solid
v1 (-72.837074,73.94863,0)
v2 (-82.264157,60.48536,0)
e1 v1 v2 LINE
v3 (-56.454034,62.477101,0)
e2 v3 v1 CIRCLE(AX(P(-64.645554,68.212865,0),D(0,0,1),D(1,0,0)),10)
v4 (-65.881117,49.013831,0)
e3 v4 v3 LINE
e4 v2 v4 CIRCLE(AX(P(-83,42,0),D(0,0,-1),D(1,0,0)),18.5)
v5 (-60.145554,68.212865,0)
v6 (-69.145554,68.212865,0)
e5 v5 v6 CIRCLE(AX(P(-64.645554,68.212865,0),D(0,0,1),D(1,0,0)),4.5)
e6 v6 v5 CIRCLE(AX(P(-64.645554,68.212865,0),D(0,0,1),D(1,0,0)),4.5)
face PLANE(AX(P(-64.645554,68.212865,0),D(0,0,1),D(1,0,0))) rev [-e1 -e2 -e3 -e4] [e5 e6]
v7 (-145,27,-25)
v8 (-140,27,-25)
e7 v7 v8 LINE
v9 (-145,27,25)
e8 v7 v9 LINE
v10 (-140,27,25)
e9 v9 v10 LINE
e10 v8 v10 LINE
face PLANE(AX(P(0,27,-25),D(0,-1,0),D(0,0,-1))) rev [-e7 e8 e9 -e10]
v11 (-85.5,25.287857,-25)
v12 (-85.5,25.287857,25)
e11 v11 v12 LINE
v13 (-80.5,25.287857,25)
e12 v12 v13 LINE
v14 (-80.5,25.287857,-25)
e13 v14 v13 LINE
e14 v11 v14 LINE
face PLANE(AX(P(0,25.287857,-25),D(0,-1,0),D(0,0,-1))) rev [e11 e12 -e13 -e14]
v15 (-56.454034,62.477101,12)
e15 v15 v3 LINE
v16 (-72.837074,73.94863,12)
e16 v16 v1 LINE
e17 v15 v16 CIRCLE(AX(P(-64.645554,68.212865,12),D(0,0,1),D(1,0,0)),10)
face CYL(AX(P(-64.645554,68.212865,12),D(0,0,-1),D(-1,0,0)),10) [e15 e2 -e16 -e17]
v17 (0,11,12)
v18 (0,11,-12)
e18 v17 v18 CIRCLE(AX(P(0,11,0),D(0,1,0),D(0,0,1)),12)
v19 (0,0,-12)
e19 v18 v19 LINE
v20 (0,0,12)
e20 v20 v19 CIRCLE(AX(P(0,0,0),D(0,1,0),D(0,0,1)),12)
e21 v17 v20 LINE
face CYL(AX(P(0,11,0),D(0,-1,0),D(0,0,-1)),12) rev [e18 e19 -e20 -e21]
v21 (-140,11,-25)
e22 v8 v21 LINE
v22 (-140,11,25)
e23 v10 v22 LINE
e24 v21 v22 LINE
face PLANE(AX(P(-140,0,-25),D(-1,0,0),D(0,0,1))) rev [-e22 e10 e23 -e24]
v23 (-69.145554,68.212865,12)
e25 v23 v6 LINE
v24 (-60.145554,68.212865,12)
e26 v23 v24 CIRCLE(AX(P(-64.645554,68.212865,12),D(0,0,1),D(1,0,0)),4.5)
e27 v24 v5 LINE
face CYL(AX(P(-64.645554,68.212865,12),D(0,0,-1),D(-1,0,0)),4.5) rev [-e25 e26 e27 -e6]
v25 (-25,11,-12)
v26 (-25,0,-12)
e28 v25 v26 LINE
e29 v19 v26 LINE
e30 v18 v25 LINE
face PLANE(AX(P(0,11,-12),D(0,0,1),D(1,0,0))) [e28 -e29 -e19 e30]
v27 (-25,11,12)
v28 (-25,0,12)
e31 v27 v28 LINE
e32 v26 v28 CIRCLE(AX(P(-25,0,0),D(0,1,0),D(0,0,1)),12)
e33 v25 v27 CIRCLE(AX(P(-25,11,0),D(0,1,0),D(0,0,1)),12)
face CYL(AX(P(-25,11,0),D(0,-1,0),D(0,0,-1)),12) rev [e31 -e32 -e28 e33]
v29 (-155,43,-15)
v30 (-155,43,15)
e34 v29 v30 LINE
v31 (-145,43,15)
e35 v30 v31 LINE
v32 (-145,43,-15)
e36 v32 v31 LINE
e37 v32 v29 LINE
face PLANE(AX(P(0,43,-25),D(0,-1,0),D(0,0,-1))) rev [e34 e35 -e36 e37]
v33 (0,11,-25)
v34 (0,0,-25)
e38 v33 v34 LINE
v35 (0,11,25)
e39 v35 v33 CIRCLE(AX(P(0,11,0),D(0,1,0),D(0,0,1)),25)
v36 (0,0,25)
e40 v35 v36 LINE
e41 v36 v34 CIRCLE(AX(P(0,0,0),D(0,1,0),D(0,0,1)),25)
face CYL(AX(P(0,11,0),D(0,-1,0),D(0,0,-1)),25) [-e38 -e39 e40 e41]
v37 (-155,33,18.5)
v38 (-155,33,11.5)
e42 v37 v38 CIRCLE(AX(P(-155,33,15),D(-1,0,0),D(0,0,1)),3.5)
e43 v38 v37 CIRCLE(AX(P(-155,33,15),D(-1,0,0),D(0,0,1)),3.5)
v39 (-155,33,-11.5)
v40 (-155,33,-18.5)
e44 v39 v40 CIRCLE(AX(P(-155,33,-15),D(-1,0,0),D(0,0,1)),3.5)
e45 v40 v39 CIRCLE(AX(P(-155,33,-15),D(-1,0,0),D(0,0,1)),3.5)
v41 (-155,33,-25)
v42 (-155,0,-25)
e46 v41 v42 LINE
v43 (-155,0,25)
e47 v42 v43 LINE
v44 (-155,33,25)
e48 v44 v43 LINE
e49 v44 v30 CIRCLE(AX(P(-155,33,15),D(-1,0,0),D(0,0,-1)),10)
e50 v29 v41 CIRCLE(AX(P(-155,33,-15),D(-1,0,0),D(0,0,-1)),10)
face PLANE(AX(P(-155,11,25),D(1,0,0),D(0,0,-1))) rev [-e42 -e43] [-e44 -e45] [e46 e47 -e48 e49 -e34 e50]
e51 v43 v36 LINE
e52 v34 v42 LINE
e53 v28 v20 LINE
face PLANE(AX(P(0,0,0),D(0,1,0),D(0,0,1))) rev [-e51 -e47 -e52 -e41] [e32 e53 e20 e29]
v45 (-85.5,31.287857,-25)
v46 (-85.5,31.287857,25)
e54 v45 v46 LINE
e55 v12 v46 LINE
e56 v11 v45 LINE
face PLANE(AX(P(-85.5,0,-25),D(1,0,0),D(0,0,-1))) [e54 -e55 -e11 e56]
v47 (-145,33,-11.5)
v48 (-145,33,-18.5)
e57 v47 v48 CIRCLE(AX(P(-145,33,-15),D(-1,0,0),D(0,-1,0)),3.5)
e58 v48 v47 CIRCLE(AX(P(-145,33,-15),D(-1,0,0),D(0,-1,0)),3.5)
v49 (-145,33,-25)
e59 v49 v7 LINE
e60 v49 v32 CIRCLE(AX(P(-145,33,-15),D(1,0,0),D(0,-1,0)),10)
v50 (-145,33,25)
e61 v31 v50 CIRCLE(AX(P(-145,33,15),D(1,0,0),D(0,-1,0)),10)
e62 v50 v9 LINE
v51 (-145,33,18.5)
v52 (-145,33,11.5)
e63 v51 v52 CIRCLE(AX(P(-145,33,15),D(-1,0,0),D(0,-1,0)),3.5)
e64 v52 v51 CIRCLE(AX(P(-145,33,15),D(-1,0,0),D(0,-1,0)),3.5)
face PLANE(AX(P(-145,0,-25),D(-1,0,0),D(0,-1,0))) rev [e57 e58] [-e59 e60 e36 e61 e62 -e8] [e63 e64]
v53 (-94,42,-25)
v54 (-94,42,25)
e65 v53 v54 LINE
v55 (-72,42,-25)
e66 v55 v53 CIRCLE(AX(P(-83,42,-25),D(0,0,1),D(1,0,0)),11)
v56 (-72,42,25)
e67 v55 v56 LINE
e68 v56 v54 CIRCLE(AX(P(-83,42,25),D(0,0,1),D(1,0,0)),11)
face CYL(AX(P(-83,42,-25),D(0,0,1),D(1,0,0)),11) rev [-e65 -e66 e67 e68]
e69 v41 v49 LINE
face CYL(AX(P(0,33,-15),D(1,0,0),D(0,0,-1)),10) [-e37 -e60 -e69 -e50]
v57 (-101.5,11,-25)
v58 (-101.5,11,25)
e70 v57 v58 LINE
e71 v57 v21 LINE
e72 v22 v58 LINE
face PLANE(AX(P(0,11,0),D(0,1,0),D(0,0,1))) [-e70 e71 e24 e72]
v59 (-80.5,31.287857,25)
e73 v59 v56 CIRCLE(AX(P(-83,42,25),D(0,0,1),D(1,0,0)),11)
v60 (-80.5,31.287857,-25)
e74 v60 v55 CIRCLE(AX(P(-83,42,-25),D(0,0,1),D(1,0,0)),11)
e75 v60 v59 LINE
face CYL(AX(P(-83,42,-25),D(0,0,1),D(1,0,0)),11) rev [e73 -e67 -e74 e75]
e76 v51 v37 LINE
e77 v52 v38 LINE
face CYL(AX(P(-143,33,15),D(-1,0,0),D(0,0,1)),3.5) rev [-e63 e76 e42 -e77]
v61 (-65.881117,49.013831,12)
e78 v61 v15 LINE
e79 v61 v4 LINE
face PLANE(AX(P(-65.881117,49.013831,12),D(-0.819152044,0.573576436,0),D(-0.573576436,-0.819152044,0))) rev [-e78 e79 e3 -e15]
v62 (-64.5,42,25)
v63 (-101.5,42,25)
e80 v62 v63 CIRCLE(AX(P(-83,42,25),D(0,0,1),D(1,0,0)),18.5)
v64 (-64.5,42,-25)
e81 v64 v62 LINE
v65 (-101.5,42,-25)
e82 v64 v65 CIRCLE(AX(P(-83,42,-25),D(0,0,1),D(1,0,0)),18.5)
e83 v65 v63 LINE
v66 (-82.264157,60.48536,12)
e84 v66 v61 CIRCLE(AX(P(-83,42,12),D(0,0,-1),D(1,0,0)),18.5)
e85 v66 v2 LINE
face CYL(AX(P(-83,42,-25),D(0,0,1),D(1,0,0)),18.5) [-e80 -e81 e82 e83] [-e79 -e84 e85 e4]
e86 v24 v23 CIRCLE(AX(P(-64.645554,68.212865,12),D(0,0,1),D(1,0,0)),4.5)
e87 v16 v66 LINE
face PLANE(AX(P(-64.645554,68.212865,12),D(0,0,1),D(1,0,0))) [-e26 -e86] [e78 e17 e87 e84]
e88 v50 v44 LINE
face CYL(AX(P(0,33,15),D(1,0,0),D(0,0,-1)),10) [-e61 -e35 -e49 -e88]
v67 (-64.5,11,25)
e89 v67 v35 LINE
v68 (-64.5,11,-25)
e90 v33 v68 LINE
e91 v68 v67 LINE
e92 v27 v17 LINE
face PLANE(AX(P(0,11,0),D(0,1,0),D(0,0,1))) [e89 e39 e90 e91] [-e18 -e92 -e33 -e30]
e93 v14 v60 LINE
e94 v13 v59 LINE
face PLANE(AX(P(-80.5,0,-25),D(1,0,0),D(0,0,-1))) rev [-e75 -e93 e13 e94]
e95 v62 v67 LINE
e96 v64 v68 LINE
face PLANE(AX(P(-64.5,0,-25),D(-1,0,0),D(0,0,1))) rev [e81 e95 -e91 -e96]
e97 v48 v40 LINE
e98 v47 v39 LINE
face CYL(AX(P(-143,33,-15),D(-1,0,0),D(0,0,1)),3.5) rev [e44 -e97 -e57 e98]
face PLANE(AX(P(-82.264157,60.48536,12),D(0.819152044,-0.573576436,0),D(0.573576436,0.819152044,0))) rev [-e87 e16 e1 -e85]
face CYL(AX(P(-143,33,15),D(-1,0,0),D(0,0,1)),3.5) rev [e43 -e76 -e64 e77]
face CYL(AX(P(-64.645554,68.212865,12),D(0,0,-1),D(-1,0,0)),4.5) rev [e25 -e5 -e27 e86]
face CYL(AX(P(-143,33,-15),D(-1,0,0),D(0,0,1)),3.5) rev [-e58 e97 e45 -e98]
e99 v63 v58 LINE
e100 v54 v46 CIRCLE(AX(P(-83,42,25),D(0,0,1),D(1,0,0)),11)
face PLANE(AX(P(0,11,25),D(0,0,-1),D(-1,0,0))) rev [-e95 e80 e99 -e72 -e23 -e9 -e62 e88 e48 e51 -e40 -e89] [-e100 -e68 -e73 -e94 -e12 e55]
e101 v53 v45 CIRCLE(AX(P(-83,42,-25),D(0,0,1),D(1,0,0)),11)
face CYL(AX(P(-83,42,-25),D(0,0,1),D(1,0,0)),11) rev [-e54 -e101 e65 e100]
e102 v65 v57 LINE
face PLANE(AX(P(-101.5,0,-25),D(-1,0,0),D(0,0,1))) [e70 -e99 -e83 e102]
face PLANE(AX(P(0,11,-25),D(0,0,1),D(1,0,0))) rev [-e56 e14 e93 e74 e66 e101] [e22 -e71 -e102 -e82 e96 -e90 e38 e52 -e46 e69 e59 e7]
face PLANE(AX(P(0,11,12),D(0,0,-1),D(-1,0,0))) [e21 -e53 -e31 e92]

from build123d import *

# Parameters (mm, degrees)
SLOTTED_BASE_PLATE_DEPTH = 11
UPRIGHT_HUB_BODY_DEPTH   = 50
CROSS_START              = 12
CROSS_BOSS_SKETCH_R      = 4.5
CROSS_BOSS_DEPTH         = 12
UPRIGHT_FILLET_R10_R     = 10
CROSS_HOLE_SKETCH_R      = 3.5
CROSS_HOLE_CUT_DEPTH     = 12


with BuildPart() as part:
    # Base Plate Sketch → Slotted Base Plate (new body)
    with BuildSketch(Plane(origin=(0, 0, 0), x_dir=(1, 0, 0), z_dir=(0, 1, 0))):
        with BuildLine():
            Line((0, 25), (-155, 25))
            Line((-155, 25), (-155, -25))
            Line((-155, -25), (0, -25))
            ThreePointArc((0, -25), (25, 0), (0, 25))
        make_face()
        with BuildLine():
            Line((0, -12), (-25, -12))
            ThreePointArc((-25, -12), (-37, 0), (-25, 12))
            Line((-25, 12), (0, 12))
            ThreePointArc((0, 12), (12, 0), (0, -12))
        make_face(mode=Mode.SUBTRACT)
    extrude(amount=SLOTTED_BASE_PLATE_DEPTH)

    # Upright Profile Sketch → Upright Hub Body (add)
    # profile 1 of 2: a face of its own
    with BuildSketch(Plane.XY.offset(25)):
        Polygon((-155, 0), (-155, 43), (-145, 43), (-145, 27), (-140, 27), (-140, 11), align=None)
    # profile 2 of 2: a face of its own
    with BuildSketch(Plane.XY.offset(25)):
        with BuildLine():
            Line((-101.5, 42), (-101.5, 11))
            Line((-101.5, 11), (-64.5, 11))
            Line((-64.5, 11), (-64.5, 42))
            ThreePointArc((-64.5, 42), (-83, 60.5), (-101.5, 42))
        make_face()
        with BuildLine():
            Line((-85.5, 25.287857357), (-80.5, 25.287857357))
            Line((-80.5, 25.287857357), (-80.5, 31.287857357))
            ThreePointArc((-80.5, 31.287857357), (-83, 53), (-85.5, 31.287857357))
            Line((-85.5, 31.287857357), (-85.5, 25.287857357))
        make_face(mode=Mode.SUBTRACT)
    extrude(amount=-UPRIGHT_HUB_BODY_DEPTH)

    # Cross Boss Sketch → Cross Boss (add)
    with BuildSketch(Plane.XY.offset(CROSS_START)):
        with BuildLine():
            Line((-65.881116557, 49.013831311), (-56.454033594, 62.477101054))
            ThreePointArc((-56.454033594, 62.477101054), (-58.909789673, 76.40438586), (-72.83707448, 73.948629781))
            Line((-72.83707448, 73.948629781), (-82.264157443, 60.485360038))
            ThreePointArc((-82.264157443, 60.485360038), (-72.388835928, 57.154312819), (-65.881116557, 49.013831311))
        make_face()
        with Locations((-64.645554037, 68.212865417)):
            Circle(CROSS_BOSS_SKETCH_R, mode=Mode.SUBTRACT)
    extrude(amount=-CROSS_BOSS_DEPTH)

    # Upright Fillet R10
    upright_fillet_r10_edges = [part.edges().sort_by_distance(p)[0] for p in [
        (-150, 43, 25),
        (-150, 43, -25),
    ]]
    fillet(upright_fillet_r10_edges, radius=UPRIGHT_FILLET_R10_R)

    # Cross Hole Sketch → Cross Hole Cut (cut)
    with BuildSketch(Plane.ZY.offset(155)):
        with Locations((15, 33)):
            Circle(CROSS_HOLE_SKETCH_R)
        with Locations((-15, 33)):
            Circle(CROSS_HOLE_SKETCH_R)
    extrude(amount=-CROSS_HOLE_CUT_DEPTH, mode=Mode.SUBTRACT)


solid = part.part
